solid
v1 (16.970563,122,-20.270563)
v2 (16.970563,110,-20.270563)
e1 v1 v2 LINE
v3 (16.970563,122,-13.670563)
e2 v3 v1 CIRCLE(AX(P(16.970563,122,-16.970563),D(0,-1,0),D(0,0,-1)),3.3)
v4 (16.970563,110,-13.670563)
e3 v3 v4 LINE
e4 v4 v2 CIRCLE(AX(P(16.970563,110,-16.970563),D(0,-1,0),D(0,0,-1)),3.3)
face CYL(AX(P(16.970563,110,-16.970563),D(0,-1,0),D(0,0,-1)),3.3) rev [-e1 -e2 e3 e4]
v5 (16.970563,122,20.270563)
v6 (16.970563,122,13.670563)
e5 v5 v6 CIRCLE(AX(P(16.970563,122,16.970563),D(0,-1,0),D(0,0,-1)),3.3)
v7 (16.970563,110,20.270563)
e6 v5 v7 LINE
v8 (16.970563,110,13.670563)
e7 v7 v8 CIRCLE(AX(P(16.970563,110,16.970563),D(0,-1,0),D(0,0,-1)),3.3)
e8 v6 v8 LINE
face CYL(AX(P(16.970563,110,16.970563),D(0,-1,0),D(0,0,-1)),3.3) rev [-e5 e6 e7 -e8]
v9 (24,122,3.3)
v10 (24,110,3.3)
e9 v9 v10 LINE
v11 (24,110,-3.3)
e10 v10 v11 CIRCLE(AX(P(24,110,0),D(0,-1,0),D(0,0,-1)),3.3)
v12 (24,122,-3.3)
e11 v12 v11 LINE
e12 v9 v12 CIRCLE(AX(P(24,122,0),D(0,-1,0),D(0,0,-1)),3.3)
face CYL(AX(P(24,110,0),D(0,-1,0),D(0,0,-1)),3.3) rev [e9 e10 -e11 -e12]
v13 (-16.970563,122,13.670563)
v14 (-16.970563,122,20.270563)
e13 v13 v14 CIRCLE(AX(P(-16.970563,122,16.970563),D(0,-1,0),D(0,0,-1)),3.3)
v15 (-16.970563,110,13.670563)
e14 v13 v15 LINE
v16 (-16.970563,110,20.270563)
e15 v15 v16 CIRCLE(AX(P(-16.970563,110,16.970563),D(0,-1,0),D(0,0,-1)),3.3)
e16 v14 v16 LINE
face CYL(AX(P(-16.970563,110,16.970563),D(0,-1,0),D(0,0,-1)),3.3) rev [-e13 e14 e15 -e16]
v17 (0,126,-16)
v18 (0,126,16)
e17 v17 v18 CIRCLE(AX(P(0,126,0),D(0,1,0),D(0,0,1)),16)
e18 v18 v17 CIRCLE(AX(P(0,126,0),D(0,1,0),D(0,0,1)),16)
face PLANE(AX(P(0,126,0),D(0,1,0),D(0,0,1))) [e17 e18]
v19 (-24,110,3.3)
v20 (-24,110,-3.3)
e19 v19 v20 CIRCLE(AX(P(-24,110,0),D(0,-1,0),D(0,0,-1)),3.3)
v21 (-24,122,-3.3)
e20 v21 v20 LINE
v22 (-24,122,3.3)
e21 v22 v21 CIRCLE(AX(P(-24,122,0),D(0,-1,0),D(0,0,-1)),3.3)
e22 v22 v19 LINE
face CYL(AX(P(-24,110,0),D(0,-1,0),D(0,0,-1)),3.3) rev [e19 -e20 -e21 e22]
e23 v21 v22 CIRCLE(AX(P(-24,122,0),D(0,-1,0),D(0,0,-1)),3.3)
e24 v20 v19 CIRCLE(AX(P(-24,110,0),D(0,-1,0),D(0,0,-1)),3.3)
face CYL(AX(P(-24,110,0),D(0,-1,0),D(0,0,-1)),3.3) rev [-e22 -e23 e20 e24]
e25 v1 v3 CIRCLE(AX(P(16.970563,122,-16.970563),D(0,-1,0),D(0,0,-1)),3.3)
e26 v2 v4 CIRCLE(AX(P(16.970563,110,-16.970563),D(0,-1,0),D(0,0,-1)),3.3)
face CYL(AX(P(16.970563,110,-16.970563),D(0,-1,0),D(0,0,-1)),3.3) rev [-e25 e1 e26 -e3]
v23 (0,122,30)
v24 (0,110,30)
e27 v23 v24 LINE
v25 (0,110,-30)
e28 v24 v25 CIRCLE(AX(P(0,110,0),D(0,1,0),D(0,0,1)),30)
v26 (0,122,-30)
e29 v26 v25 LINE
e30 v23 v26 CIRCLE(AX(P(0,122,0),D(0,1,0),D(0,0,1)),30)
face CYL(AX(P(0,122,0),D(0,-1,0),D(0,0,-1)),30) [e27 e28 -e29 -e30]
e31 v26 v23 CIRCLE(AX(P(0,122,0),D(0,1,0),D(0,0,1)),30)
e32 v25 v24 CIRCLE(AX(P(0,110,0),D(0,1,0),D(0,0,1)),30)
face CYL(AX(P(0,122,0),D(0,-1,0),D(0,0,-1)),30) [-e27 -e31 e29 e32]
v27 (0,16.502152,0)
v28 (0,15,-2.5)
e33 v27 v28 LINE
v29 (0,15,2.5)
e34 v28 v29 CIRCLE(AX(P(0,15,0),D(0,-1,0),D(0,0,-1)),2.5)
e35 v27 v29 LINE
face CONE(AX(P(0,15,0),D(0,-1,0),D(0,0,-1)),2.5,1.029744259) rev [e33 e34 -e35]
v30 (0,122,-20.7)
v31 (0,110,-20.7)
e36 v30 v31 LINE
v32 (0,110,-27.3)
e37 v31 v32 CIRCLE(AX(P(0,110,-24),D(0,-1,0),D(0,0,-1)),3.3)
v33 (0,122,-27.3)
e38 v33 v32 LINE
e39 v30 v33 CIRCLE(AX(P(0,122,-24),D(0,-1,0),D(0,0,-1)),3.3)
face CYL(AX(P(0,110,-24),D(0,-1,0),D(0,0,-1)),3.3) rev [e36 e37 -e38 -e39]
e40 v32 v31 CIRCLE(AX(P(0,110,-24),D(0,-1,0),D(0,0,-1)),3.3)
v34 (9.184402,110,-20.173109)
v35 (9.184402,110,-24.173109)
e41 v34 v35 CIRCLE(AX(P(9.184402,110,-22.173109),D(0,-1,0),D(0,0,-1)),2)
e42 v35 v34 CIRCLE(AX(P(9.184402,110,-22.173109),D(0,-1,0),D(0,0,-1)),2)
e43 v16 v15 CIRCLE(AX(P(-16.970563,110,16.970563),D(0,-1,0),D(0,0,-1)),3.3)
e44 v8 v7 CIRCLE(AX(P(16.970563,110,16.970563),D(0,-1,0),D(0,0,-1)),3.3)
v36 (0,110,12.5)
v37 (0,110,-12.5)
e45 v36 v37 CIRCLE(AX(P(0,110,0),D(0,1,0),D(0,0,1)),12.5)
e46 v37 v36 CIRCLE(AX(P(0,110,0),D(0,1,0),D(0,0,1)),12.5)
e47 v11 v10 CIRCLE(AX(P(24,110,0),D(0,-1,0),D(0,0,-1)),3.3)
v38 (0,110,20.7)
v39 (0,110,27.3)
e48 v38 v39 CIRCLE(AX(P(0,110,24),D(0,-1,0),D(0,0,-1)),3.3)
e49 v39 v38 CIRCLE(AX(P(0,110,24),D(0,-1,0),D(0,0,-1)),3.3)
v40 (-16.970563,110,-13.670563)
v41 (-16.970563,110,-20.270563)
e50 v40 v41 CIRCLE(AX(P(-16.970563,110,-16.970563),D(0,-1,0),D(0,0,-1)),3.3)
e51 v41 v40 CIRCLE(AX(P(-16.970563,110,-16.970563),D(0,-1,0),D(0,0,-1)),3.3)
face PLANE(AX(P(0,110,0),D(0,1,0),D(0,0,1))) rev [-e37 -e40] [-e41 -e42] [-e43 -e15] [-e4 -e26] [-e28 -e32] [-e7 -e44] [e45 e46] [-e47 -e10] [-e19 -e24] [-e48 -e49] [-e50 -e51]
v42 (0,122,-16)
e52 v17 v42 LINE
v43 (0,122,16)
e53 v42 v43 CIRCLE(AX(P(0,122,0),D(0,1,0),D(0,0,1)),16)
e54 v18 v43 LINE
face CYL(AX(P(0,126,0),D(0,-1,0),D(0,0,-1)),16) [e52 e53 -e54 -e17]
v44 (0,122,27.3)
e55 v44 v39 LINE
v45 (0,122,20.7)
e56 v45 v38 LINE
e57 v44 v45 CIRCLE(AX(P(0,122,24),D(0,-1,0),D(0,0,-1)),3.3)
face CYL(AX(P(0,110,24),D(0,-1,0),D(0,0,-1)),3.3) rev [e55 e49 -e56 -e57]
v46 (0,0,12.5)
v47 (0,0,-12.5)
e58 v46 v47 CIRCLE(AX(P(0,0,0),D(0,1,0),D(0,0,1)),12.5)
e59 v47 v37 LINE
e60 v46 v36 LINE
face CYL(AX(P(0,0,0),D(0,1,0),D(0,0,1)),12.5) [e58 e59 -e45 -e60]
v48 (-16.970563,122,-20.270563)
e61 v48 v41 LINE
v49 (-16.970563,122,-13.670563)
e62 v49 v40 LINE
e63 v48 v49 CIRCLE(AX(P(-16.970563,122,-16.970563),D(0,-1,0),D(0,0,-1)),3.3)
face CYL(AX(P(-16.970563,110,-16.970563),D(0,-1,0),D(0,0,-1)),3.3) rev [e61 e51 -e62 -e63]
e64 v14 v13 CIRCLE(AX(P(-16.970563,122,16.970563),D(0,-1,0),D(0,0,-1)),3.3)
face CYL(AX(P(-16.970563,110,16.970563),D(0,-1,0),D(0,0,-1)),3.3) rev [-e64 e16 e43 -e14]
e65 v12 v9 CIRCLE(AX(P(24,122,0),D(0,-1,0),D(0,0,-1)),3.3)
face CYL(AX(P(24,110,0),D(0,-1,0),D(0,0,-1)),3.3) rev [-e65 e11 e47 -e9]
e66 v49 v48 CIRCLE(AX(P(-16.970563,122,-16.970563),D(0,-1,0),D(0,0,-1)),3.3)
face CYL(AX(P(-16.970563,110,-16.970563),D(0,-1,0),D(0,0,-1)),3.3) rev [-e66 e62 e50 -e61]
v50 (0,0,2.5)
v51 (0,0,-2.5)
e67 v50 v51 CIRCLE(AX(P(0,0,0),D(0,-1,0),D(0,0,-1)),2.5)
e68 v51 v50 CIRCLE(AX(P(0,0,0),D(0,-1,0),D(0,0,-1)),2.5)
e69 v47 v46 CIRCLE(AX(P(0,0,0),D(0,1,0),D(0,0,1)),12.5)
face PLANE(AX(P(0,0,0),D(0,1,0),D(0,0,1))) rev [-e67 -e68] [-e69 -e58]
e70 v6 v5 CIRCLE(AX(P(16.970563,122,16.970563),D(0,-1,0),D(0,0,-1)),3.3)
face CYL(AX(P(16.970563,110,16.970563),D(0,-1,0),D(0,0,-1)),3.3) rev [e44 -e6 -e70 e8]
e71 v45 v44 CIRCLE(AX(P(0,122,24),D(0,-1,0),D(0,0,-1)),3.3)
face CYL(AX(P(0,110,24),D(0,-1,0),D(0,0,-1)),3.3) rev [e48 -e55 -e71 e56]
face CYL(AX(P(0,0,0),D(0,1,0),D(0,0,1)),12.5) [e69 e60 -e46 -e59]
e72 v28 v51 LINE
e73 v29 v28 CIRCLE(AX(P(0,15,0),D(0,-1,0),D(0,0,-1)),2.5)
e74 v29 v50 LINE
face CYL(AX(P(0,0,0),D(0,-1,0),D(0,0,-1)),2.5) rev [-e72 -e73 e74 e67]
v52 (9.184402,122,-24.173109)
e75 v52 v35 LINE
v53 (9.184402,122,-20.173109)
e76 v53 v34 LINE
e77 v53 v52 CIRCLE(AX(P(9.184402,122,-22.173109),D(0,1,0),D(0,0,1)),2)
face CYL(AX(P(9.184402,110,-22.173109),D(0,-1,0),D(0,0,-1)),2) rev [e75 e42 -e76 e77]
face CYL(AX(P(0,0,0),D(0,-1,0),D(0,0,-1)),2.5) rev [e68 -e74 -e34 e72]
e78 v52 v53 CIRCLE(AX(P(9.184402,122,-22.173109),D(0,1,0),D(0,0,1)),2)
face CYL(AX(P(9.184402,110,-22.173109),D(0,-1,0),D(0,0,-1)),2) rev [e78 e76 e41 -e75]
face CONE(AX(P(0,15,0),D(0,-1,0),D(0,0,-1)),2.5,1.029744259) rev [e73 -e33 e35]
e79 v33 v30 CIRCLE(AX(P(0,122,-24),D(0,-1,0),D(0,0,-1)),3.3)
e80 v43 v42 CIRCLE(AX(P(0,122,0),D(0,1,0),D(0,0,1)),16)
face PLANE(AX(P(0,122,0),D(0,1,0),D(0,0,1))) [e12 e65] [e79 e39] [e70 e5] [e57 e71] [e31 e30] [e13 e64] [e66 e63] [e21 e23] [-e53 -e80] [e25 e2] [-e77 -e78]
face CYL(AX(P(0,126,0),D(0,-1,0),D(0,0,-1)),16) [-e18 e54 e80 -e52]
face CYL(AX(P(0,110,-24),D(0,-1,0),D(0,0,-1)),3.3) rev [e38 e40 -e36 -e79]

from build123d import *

# Parameters (mm, degrees)
SKETCH_1_R               = 30
EXTRUDE_1_DEPTH          = 122
CUT_EXTRUDE_START        = -12
SKETCH_2_OUTSIDE_W       = 91.722
SKETCH_2_OUTSIDE_H       = 91.722
SKETCH_2_OUTSIDE_R       = 12.5
CUT_EXTRUDE_1_DEPTH      = 118.16655914
HOLE_WIZARD_M6_1_D       = 6.6
SKETCH_7_R               = 16
EXTRUDE_3_DEPTH          = 4
MM_0_D                   = 4
HOLE_WIZARD_M6_1_2_D     = 5
HOLE_WIZARD_M6_1_2_DEPTH = 15
HOLE_WIZARD_M6_1_2_TIP   = 1.502151548


with BuildPart() as part:
    # 草图1 → 凸台-拉伸1 (new body)
    with BuildSketch(Plane(origin=(0, 0, 0), x_dir=(1, 0, 0), z_dir=(0, 1, 0))):
        with Locations(Location((0, 0, 0), (0, 0, 90))):
            Circle(SKETCH_1_R)
    extrude(amount=EXTRUDE_1_DEPTH)

    # 草图2 outside → 切除-拉伸1 (cut, through all)
    with BuildSketch(Plane(origin=(0, 122, 0), x_dir=(1, 0, 0), z_dir=(0, 1, 0)).offset(CUT_EXTRUDE_START)):
        Rectangle(SKETCH_2_OUTSIDE_W, SKETCH_2_OUTSIDE_H)
        with Locations(Location((0, 0, 0), (0, 0, 270))):
            Circle(SKETCH_2_OUTSIDE_R, mode=Mode.SUBTRACT)
    extrude(amount=-CUT_EXTRUDE_1_DEPTH, mode=Mode.SUBTRACT)

    # Hole Wizard M6 _1 (through all)
    with Locations(Plane(origin=(0, 110, 0), x_dir=(-1, 0, 0), z_dir=(0, -1, 0))):
        with Locations((-24, 0), (-16.970562748, 16.970562748), (0, 24), (16.970562748, 16.970562748), (24, 0), (16.970562748, -16.970562748), (0, -24), (-16.970562748, -16.970562748)):
            Hole(HOLE_WIZARD_M6_1_D / 2)

    # 草图7 → 凸台-拉伸3 (add)
    with BuildSketch(Plane(origin=(0, 122, 0), x_dir=(1, 0, 0), z_dir=(0, 1, 0))):
        with Locations(Location((0, 0, 0), (0, 0, 270))):
            Circle(SKETCH_7_R)
    extrude(amount=EXTRUDE_3_DEPTH)

    # 大小mm 暗销孔0 (through all)
    with Locations(Plane(origin=(0, 110, 0), x_dir=(-1, 0, 0), z_dir=(0, -1, 0))):
        with Locations((-9.184402377, 22.17310878)):
            Hole(MM_0_D / 2)

    # Hole Wizard M6 _1 2
    with Locations(Plane(origin=(0, 0, 0), x_dir=(-1, 0, 0), z_dir=(0, -1, 0))):
        with Locations((0, 0)):
            Hole(HOLE_WIZARD_M6_1_2_D / 2, depth=HOLE_WIZARD_M6_1_2_DEPTH)
            with Locations((0, 0, -(HOLE_WIZARD_M6_1_2_DEPTH + HOLE_WIZARD_M6_1_2_TIP / 2))):  # 118° drill point
                Cone(0, HOLE_WIZARD_M6_1_2_D / 2, HOLE_WIZARD_M6_1_2_TIP, mode=Mode.SUBTRACT)


solid = part.part
